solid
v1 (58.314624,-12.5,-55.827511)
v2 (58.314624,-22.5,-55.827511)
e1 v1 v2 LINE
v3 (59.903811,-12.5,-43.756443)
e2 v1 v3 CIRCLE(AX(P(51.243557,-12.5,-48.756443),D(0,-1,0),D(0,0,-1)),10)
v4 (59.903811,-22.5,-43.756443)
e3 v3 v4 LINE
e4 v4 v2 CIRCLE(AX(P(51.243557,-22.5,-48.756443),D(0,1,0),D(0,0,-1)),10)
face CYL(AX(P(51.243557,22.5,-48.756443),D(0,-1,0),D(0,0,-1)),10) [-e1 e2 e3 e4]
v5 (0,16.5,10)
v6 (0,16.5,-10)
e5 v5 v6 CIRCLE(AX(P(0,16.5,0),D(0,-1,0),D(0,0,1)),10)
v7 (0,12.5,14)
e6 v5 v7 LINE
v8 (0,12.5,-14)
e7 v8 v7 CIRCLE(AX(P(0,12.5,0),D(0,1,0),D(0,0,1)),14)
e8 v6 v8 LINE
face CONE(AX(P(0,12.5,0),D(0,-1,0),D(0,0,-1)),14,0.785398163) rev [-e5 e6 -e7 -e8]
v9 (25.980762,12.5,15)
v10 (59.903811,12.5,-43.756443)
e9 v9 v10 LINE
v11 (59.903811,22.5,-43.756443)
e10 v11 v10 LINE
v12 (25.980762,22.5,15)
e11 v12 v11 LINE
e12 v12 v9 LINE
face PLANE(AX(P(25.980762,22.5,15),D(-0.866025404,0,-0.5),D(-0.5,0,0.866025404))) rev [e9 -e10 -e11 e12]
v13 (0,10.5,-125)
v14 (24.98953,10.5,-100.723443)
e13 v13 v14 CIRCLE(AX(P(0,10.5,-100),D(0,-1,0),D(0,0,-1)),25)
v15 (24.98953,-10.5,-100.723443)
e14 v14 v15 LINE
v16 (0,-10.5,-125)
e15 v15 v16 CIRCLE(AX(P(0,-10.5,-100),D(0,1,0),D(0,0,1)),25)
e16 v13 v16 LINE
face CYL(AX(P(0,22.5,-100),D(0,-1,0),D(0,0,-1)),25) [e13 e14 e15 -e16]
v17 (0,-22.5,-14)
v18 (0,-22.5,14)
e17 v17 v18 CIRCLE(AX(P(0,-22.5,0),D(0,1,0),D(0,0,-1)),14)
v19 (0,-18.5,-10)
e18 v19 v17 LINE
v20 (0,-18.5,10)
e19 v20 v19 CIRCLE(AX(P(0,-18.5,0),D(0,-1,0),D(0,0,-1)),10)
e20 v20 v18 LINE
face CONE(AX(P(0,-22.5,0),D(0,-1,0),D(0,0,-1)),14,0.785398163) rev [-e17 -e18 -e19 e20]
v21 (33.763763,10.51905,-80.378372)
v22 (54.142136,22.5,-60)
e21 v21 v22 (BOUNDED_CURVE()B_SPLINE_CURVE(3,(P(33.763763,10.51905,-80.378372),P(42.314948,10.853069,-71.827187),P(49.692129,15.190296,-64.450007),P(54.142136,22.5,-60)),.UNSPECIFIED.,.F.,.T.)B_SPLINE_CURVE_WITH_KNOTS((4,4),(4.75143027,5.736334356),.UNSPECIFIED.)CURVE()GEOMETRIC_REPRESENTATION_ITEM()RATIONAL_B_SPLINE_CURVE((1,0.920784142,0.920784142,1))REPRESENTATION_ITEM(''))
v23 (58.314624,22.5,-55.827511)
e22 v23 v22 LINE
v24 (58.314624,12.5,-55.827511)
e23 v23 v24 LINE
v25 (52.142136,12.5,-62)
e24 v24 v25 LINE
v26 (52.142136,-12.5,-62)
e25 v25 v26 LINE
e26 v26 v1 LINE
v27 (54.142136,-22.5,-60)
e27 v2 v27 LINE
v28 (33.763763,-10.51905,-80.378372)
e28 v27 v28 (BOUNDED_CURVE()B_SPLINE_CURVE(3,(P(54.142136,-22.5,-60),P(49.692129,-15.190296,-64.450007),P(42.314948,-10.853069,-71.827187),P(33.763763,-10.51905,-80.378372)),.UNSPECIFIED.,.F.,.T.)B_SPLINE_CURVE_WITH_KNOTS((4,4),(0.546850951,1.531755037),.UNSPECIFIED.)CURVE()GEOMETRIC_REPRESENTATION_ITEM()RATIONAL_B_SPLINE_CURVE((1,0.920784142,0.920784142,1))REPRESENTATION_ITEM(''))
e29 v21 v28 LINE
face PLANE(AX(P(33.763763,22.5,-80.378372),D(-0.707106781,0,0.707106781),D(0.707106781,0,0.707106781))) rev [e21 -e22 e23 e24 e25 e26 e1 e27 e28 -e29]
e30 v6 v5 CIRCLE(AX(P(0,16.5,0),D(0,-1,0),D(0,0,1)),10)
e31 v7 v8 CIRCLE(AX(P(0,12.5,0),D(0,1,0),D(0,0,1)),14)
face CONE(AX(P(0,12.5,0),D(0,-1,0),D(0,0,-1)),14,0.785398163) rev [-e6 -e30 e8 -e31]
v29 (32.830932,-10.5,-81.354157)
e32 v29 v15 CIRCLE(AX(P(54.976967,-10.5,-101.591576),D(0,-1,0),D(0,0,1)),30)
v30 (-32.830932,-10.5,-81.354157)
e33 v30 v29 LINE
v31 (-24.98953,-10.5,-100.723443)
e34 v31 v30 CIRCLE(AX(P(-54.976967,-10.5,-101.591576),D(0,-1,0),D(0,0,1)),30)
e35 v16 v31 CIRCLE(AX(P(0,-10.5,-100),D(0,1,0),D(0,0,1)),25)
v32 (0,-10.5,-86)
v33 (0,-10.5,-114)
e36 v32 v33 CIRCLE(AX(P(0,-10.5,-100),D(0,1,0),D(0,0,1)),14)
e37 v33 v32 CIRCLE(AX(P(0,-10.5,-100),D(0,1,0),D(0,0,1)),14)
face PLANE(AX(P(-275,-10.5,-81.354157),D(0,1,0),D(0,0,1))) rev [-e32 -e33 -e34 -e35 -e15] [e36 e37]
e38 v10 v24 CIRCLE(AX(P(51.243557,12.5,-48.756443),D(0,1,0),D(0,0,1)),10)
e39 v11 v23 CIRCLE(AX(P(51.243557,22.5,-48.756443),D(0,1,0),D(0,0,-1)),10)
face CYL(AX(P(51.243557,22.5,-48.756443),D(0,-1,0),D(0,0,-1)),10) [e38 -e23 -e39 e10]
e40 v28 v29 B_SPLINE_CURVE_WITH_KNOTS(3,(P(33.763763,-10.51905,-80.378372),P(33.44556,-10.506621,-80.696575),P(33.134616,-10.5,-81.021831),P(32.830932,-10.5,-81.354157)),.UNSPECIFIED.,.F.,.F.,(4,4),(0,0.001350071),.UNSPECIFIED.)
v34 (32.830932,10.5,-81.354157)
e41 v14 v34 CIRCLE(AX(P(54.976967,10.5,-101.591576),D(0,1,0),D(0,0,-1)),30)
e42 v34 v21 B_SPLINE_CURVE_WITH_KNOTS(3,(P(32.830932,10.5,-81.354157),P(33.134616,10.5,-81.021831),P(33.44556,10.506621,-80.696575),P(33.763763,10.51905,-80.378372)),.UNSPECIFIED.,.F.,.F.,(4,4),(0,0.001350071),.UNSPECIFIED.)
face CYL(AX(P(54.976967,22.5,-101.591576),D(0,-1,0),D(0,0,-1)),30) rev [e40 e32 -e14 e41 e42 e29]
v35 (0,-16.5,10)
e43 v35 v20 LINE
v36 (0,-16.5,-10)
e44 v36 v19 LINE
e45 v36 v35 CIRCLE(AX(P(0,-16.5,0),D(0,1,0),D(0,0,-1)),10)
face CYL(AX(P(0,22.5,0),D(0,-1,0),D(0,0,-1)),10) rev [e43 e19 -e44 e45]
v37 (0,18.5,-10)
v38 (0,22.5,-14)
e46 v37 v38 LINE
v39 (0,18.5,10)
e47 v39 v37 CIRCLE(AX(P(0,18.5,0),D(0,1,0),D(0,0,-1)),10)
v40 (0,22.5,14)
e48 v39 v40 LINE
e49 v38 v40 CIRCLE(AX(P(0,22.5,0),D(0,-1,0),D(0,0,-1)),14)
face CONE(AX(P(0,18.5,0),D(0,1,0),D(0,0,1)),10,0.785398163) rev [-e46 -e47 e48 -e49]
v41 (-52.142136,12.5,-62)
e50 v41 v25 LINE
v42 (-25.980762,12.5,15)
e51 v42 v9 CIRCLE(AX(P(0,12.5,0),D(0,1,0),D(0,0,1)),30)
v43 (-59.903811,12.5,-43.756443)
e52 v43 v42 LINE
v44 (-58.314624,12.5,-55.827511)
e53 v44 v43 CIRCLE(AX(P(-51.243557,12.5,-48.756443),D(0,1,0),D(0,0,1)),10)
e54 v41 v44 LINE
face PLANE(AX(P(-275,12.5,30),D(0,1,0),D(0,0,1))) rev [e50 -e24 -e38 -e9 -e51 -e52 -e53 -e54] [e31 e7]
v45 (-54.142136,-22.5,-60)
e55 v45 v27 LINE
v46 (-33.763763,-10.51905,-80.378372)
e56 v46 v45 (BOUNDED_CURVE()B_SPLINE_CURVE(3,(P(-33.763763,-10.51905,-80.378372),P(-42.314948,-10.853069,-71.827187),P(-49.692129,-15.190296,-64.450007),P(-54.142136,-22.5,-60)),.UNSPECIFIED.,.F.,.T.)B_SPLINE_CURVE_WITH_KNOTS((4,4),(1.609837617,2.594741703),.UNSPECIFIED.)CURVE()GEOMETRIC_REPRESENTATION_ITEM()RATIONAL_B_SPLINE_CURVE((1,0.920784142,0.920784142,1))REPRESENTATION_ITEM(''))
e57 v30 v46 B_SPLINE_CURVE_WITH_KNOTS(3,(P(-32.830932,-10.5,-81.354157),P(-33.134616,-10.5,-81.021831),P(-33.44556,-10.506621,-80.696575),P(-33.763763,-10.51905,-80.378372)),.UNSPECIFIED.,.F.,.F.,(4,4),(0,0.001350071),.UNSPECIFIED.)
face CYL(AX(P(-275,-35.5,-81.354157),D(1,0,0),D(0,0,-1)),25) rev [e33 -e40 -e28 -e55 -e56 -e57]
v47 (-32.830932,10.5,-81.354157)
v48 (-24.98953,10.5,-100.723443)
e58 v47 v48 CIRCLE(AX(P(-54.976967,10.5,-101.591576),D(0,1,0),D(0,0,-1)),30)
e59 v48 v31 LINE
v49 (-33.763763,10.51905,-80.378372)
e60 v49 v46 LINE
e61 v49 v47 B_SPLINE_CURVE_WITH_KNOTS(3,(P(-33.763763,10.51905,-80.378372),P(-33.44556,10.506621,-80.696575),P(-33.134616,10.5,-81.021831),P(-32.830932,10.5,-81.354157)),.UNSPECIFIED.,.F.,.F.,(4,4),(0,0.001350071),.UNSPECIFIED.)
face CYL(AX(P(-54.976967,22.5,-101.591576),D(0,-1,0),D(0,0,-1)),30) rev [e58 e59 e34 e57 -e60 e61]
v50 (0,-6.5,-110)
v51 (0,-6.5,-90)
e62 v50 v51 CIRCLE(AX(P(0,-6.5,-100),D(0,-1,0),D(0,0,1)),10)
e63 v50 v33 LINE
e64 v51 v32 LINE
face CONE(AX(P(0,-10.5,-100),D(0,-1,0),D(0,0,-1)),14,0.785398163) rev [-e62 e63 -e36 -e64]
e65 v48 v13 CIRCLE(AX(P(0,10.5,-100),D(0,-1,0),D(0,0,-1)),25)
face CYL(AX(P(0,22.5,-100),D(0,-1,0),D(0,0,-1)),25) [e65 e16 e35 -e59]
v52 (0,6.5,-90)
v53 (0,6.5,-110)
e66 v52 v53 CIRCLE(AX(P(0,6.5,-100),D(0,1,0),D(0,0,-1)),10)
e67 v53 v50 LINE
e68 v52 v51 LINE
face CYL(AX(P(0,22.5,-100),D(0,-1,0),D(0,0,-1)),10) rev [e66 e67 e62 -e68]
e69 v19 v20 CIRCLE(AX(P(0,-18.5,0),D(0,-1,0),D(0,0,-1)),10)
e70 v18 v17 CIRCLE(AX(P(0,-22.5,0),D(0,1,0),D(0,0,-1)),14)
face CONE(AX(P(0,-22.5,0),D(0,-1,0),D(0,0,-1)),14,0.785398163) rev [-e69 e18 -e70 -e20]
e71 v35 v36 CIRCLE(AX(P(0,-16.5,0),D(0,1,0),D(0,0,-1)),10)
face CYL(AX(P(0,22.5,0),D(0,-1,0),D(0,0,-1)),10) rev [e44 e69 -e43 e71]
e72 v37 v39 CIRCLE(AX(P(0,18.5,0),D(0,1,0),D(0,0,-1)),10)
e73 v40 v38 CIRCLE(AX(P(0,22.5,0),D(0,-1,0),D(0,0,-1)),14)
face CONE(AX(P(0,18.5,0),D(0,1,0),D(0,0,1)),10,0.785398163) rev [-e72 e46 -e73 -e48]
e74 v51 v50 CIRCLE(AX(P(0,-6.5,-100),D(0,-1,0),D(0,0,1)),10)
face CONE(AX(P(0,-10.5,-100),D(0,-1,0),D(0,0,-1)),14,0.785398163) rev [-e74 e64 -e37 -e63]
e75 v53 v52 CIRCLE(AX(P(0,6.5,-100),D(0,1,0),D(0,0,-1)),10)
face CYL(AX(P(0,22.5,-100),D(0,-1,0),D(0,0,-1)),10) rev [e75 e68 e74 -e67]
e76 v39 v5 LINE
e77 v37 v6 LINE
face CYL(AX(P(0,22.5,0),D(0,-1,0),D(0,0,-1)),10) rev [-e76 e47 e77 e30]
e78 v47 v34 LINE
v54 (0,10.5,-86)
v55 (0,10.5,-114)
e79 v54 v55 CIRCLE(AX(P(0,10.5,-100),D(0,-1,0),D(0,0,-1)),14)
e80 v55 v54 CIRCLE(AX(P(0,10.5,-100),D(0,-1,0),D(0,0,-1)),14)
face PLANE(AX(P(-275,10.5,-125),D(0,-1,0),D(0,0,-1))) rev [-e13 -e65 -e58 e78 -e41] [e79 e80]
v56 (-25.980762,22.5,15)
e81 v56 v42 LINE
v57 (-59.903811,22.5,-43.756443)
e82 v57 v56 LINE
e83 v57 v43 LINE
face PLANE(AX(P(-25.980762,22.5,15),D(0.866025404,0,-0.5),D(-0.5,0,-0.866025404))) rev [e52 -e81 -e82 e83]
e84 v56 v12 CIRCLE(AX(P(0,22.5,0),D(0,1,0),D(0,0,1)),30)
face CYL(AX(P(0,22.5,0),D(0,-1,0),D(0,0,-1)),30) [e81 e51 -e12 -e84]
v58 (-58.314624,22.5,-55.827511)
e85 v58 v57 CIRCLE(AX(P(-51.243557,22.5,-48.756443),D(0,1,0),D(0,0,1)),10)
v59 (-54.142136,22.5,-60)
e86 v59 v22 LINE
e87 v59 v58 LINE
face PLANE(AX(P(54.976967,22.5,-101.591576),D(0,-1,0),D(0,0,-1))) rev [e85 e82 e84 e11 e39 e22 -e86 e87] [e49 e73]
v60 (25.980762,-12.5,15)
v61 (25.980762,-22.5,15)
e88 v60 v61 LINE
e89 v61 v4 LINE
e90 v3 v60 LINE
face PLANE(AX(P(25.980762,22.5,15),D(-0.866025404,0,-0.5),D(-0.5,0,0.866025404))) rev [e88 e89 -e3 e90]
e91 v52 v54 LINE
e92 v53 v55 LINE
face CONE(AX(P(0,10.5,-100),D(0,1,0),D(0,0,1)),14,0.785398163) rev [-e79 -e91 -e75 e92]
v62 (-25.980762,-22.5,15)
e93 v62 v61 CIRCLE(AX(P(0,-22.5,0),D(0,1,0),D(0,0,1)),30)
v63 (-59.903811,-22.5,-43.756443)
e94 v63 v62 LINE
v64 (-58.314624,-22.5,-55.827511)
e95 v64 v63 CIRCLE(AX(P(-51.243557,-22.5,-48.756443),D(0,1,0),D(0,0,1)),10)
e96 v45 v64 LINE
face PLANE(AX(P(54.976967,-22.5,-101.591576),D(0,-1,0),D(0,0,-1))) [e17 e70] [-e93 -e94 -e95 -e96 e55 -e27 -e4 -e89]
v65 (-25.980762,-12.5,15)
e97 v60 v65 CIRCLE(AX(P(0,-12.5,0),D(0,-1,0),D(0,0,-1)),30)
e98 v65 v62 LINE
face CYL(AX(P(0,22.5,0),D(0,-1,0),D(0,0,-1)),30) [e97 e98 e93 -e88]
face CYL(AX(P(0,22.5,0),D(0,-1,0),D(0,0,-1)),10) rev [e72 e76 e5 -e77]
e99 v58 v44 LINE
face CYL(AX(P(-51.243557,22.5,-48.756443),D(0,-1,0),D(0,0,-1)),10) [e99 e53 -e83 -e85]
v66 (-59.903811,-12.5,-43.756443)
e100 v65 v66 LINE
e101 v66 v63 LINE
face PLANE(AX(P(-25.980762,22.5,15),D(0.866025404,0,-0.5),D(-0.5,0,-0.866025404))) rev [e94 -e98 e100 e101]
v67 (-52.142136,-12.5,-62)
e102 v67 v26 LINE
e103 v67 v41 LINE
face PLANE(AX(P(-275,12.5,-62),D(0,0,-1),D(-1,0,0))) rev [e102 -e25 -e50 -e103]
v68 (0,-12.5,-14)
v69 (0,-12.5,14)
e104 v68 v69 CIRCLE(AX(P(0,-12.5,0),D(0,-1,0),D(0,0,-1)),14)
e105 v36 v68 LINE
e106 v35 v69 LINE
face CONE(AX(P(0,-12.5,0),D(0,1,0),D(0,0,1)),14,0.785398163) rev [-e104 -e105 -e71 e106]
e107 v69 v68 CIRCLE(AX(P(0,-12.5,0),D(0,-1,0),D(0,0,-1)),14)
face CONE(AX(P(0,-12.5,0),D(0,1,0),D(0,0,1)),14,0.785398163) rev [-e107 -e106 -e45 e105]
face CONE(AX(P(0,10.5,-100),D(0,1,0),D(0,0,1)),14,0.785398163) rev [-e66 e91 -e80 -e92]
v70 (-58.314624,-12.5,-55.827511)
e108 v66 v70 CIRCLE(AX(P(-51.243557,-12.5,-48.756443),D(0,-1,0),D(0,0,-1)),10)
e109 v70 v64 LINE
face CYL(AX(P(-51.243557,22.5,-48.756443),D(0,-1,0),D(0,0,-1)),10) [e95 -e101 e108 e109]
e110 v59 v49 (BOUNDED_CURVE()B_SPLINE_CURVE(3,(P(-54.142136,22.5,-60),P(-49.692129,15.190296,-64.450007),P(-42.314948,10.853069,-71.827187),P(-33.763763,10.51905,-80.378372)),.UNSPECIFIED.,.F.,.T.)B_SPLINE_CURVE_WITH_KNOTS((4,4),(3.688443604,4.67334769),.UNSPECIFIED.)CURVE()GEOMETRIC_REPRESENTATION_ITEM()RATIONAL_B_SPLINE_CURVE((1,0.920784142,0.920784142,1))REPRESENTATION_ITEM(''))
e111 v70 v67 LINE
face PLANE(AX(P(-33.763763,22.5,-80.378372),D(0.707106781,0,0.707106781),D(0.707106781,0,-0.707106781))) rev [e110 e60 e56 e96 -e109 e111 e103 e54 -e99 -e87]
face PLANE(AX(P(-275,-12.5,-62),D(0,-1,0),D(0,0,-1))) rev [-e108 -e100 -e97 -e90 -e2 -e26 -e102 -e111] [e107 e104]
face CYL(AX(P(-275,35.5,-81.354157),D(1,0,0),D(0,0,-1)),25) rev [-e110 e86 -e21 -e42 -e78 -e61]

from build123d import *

# Parameters (mm, degrees)
BRACKET_PROFILE_SKETCH_R     = 10
BRACKET_BODY_DEPTH           = 22.5
CLEVIS_SLOT_SKETCH_W         = 92
CLEVIS_SLOT_SKETCH_H         = 25
CLEVIS_SLOT_10MM_DEPTH       = 375
RELIEF_CUT_DEPTH             = 375
BODY_EDGE_CHAMFER_4MM_A_SIZE = 4
SLOT_EDGE_CHAMFER_4MM_A_SIZE = 4
BODY_EDGE_CHAMFER_4MM_B_SIZE = 4
SLOT_EDGE_CHAMFER_4MM_B_SIZE = 4
RELIEF_CUT_CHAMFER_4MM_SIZE  = 4


with BuildPart() as part:
    # Bracket Profile Sketch → Bracket Body (new, symmetric)
    with BuildSketch(Plane(origin=(0, 0, 0), x_dir=(1, 0, 0), z_dir=(0, 1, 0))):
        with BuildLine():
            Line((-33.763763442, 80.378372182), (-58.314624342, 55.827511282))
            ThreePointArc((-58.314624342, 55.827511282), (-61.158005144, 50.061705392), (-59.903810568, 43.75644347))
            Line((-59.903810568, 43.75644347), (-25.980762114, -15))
            ThreePointArc((-25.980762114, -15), (0, -30), (25.980762114, -15))
            Line((25.980762114, -15), (59.903810568, 43.75644347))
            ThreePointArc((59.903810568, 43.75644347), (61.158005144, 50.061705392), (58.314624342, 55.827511282))
            Line((58.314624342, 55.827511282), (33.763763442, 80.378372182))
            ThreePointArc((33.763763442, 80.378372182), (27.429610139, 89.711207915), (24.989530399, 100.723443462))
            ThreePointArc((24.989530399, 100.723443462), (0, 125), (-24.989530399, 100.723443462))
            ThreePointArc((-24.989530399, 100.723443462), (-27.429610139, 89.711207915), (-33.763763442, 80.378372182))
        make_face()
        with Locations(Location((0, 0, 0), (0, 0, 90))):
            Circle(BRACKET_PROFILE_SKETCH_R, mode=Mode.SUBTRACT)
        with Locations(Location((0, 100, 0), (0, 0, 90))):
            Circle(BRACKET_PROFILE_SKETCH_R, mode=Mode.SUBTRACT)
    extrude(amount=BRACKET_BODY_DEPTH, both=True)

    # Clevis Slot Sketch → Clevis Slot 10mm (cut)
    with BuildSketch(Plane(origin=(100, 0, 0), x_dir=(0, 0, -1), z_dir=(1, 0, 0))):
        with Locations((16, 0)):
            Rectangle(CLEVIS_SLOT_SKETCH_W, CLEVIS_SLOT_SKETCH_H)
    extrude(amount=-CLEVIS_SLOT_10MM_DEPTH, mode=Mode.SUBTRACT)

    # Relief Cut Sketch → Relief Cut (cut)
    with BuildSketch(Plane(origin=(100, 0, 0), x_dir=(0, 0, -1), z_dir=(1, 0, 0))):
        with BuildLine():
            Line((60, 22.5), (125, 22.5))
            Line((125, 22.5), (125, 10.5))
            Line((125, 10.5), (81.354156504, 10.5))
            ThreePointArc((81.354156504, 10.5), (69.10670779, 13.705505282), (60, 22.5))
        make_face()
        with BuildLine():
            Line((81.354156504, -10.5), (125, -10.5))
            Line((125, -10.5), (125, -22.5))
            Line((125, -22.5), (60, -22.5))
            ThreePointArc((60, -22.5), (69.10670779, -13.705505282), (81.354156504, -10.5))
        make_face()
    extrude(amount=-RELIEF_CUT_DEPTH, mode=Mode.SUBTRACT)

    # Body Edge Chamfer 4mm A
    body_edge_chamfer_4mm_a_edges = [part.edges().sort_by_distance(p)[0] for p in [
        (0, 22.5, 10),
    ]]
    chamfer(body_edge_chamfer_4mm_a_edges, length=BODY_EDGE_CHAMFER_4MM_A_SIZE)

    # Slot Edge Chamfer 4mm A
    slot_edge_chamfer_4mm_a_edges = [part.edges().sort_by_distance(p)[0] for p in [
        (0, 12.5, 10),
    ]]
    chamfer(slot_edge_chamfer_4mm_a_edges, length=SLOT_EDGE_CHAMFER_4MM_A_SIZE)

    # Body Edge Chamfer 4mm B
    body_edge_chamfer_4mm_b_edges = [part.edges().sort_by_distance(p)[0] for p in [
        (0, -22.5, 10),
    ]]
    chamfer(body_edge_chamfer_4mm_b_edges, length=BODY_EDGE_CHAMFER_4MM_B_SIZE)

    # Slot Edge Chamfer 4mm B
    slot_edge_chamfer_4mm_b_edges = [part.edges().sort_by_distance(p)[0] for p in [
        (0, -12.5, 10),
    ]]
    chamfer(slot_edge_chamfer_4mm_b_edges, length=SLOT_EDGE_CHAMFER_4MM_B_SIZE)

    # Relief Cut Chamfer 4mm
    relief_cut_chamfer_4mm_edges = [part.edges().sort_by_distance(p)[0] for p in [
        (0, 10.5, -90),
        (0, -10.5, -90),
    ]]
    chamfer(relief_cut_chamfer_4mm_edges, length=RELIEF_CUT_CHAMFER_4MM_SIZE)


solid = part.part
